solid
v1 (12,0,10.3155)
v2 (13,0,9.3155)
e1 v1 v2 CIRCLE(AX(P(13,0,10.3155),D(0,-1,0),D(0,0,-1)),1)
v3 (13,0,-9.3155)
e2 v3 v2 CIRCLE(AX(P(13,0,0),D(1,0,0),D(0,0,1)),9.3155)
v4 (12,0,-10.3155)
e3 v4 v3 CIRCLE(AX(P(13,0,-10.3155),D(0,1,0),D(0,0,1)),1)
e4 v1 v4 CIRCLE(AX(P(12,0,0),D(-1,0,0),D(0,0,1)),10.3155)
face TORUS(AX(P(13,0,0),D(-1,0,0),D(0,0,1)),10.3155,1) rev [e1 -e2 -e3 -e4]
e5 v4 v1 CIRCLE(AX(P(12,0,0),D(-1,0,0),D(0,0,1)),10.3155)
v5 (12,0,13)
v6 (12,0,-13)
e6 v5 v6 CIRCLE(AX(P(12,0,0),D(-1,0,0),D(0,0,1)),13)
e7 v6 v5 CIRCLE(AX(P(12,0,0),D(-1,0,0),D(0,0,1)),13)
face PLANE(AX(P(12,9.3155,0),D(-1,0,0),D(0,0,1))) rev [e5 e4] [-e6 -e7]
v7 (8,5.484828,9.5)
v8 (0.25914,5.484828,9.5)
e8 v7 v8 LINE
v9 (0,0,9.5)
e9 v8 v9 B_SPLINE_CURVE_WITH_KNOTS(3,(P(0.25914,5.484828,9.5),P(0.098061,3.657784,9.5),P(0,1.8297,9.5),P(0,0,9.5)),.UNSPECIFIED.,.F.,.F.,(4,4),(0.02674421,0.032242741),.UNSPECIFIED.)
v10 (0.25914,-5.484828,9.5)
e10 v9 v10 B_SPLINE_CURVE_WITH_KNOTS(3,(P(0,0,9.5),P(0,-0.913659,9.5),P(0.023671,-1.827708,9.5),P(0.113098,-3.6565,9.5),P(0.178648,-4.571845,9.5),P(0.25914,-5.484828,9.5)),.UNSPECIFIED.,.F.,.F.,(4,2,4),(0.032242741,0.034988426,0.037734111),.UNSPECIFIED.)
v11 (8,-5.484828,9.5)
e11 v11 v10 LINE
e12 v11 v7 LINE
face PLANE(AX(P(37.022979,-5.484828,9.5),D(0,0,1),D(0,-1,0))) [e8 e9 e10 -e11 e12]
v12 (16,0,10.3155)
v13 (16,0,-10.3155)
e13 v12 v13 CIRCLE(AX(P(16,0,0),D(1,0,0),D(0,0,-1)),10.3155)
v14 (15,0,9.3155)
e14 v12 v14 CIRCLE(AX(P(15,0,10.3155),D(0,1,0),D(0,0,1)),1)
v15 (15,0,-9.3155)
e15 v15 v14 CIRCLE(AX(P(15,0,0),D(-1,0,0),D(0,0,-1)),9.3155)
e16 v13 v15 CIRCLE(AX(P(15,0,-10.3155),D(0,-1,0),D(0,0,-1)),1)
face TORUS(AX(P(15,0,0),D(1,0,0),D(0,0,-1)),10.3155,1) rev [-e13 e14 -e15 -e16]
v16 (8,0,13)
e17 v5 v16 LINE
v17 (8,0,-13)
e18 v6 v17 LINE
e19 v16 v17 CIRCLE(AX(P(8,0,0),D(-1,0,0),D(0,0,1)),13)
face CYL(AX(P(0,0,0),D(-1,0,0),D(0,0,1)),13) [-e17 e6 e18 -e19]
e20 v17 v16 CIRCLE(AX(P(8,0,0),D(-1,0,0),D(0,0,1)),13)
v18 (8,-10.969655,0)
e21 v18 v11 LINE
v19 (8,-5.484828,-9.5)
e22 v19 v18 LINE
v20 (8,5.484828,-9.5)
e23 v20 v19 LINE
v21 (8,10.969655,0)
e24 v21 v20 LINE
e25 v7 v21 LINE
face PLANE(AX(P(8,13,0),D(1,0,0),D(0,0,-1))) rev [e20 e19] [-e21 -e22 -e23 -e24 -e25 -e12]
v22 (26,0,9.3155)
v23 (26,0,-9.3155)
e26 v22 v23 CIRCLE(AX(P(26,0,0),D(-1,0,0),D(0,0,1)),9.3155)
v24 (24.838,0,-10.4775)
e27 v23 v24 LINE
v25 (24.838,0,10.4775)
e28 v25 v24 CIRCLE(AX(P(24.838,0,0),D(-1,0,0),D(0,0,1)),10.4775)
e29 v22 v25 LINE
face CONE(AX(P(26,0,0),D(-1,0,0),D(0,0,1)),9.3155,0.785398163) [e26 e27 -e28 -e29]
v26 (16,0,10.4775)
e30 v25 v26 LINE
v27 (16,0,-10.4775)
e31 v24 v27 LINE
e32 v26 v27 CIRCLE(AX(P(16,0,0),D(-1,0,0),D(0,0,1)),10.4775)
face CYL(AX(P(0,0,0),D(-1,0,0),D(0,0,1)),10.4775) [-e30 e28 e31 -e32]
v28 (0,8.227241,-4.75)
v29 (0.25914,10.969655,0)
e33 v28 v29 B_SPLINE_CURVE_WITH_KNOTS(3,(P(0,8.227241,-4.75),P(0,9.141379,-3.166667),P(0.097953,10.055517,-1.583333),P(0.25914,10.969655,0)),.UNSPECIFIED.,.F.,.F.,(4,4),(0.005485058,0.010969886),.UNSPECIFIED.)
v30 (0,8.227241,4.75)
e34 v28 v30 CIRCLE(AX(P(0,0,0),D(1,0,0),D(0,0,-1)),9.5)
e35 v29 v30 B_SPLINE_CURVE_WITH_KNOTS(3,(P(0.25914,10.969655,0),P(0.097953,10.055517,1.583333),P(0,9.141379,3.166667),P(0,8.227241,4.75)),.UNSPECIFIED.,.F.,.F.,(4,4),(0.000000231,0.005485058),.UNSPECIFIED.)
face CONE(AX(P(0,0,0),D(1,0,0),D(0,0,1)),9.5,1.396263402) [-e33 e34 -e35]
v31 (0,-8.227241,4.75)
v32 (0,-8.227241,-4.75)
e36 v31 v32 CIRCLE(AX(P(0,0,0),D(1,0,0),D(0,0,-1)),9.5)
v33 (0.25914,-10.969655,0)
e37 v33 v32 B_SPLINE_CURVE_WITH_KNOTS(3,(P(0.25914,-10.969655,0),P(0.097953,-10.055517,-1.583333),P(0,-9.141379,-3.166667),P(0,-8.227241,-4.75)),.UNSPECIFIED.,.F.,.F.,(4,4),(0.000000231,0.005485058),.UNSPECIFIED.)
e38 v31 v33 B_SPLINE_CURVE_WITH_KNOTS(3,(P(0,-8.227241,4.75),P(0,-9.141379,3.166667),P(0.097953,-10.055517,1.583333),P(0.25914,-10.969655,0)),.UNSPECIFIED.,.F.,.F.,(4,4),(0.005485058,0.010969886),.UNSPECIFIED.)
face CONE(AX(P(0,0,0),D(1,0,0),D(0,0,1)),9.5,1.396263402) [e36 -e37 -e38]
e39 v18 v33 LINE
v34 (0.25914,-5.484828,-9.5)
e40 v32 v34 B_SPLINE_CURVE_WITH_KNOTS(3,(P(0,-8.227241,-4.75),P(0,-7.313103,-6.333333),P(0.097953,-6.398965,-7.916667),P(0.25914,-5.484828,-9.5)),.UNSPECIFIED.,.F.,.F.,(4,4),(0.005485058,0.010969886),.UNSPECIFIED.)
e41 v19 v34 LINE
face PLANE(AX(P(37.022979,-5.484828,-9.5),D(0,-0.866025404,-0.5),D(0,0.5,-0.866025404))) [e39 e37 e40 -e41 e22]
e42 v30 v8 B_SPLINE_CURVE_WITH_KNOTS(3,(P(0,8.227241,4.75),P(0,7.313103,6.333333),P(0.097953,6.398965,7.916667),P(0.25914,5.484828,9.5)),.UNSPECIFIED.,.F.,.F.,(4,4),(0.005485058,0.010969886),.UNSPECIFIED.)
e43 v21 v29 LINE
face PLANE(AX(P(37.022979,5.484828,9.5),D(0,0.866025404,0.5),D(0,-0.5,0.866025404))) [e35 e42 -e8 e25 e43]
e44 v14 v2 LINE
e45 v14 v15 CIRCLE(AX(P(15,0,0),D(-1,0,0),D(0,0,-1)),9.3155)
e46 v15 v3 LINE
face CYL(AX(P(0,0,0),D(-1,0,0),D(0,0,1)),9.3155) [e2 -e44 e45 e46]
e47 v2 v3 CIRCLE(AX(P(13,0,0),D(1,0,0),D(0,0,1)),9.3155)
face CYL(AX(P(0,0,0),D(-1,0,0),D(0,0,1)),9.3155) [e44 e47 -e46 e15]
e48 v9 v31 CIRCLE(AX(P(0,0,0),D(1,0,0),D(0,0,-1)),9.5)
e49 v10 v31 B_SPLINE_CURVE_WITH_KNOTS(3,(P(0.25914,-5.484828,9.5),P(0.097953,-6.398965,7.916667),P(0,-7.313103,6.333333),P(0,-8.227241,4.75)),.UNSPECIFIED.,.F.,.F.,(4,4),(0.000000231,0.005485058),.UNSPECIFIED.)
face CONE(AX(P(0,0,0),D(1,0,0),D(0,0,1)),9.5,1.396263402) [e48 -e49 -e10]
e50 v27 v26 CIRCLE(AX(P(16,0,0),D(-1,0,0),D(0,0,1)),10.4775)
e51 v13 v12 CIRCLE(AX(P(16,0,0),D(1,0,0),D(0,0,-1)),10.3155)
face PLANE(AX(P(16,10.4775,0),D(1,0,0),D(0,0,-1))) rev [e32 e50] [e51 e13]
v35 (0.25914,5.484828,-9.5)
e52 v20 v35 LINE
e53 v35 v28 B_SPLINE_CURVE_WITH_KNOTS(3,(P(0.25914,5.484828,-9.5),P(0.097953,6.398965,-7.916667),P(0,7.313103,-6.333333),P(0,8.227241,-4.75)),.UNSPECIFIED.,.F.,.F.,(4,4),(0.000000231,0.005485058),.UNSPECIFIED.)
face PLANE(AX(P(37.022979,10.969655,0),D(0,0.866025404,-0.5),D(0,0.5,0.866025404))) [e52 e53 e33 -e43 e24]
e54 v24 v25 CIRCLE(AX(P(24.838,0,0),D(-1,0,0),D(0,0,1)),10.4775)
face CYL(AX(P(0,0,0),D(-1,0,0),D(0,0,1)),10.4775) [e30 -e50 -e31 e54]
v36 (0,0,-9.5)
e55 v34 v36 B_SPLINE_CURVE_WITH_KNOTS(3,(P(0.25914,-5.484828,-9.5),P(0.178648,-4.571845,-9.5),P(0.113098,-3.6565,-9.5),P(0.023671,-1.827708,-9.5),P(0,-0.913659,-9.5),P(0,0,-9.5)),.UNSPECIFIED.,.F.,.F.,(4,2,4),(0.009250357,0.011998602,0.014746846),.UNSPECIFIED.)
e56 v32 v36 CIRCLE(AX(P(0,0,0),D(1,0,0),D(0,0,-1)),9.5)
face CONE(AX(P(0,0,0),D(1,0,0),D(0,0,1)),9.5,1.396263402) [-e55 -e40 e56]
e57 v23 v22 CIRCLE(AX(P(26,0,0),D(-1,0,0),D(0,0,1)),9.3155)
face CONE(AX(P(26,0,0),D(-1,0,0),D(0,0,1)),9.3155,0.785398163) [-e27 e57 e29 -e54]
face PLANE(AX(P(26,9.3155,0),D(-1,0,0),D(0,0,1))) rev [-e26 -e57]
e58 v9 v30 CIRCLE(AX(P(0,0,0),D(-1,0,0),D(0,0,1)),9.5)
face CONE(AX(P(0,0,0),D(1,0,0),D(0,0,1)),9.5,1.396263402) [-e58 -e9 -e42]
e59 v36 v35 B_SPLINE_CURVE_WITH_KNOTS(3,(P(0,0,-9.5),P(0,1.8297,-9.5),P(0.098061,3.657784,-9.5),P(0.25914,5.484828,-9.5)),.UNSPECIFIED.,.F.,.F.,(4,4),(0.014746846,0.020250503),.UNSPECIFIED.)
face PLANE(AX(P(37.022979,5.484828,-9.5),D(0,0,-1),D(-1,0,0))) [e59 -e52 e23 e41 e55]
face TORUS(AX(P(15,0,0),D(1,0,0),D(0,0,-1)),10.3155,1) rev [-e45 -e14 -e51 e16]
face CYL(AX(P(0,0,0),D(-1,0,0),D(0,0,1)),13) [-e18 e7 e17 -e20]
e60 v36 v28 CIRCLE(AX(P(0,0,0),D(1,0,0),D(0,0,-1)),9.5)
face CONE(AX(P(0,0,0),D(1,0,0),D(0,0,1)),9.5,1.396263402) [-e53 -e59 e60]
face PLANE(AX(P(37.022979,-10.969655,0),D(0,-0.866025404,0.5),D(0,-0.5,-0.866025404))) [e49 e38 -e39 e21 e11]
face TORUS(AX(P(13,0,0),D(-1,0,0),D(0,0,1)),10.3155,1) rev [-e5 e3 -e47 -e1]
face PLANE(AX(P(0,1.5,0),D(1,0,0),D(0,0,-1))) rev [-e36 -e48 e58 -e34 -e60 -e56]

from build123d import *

# Parameters (mm, degrees)
EXTRUDE1_DEPTH     = 8
SKETCH3_OUTSIDE_W  = 150.432
SKETCH3_OUTSIDE_H  = 150.432
SKETCH3_OUTSIDE_R  = 9.5
CUT_EXTRUDE1_DEPTH = 10
CUT_EXTRUDE1_DRAFT = -80
FILLET1_R          = 1


with BuildPart() as part:
    # Sketch1 → Revolve1 (revolve)
    with BuildSketch(Plane.XY, mode=Mode.PRIVATE) as revolve1_sk:
        Polygon((16, 10.4775), (16, 9.3155), (12, 9.3155), (12, 13), (8, 13), (8, 1.5), (0, 1.5), (0, 0), (26, 0), (26, 9.3155), (24.838, 10.4775), align=None)
    revolve(revolve1_sk.sketch.rotate(Axis((0, 0, 0), (1, 0, 0)), 90), axis=Axis((0, 0, 0), (1, 0, 0)))

    # Sketch2 → Extrude1 (add)
    with BuildSketch(Plane.ZY):
        Polygon((0, 10.969655115), (-9.5, 5.484827557), (-9.5, -5.484827557), (0, -10.969655115), (9.5, -5.484827557), (9.5, 5.484827557), align=None)
    extrude(amount=-EXTRUDE1_DEPTH)


with BuildPart() as cut_extrude1_tool:
    # Sketch3 outside → Cut-Extrude1 (with draft: the straight prism first)
    with BuildSketch(Plane.ZY):
        Rectangle(SKETCH3_OUTSIDE_W, SKETCH3_OUTSIDE_H)
        Circle(SKETCH3_OUTSIDE_R, mode=Mode.SUBTRACT)
    extrude(amount=-CUT_EXTRUDE1_DEPTH)
    # Cut-Extrude1: the draft: its side faces are tilted about the plane it starts from
    cut_extrude1_sides = [cut_extrude1_tool.faces().sort_by_distance(p)[0] for p in [
        (5, -75.216, 0),
        (5, 0, 75.216),
        (5, 75.216, 0),
        (5, 0, -75.216),
        (5, 0, -9.5),
    ]]
    draft(cut_extrude1_sides, Plane.ZY, CUT_EXTRUDE1_DRAFT)


with BuildPart() as part_1:
    add(part.part)

    # Cut-Extrude1: cut by cut_extrude1_tool
    add(cut_extrude1_tool.part, mode=Mode.SUBTRACT)

    # Fillet1
    fillet1_edges = [part_1.edges().sort_by_distance(p)[0] for p in [
        (16, 0, -9.3155),
        (12, 0, -9.3155),
    ]]
    fillet(fillet1_edges, radius=FILLET1_R)


solid = part_1.part
